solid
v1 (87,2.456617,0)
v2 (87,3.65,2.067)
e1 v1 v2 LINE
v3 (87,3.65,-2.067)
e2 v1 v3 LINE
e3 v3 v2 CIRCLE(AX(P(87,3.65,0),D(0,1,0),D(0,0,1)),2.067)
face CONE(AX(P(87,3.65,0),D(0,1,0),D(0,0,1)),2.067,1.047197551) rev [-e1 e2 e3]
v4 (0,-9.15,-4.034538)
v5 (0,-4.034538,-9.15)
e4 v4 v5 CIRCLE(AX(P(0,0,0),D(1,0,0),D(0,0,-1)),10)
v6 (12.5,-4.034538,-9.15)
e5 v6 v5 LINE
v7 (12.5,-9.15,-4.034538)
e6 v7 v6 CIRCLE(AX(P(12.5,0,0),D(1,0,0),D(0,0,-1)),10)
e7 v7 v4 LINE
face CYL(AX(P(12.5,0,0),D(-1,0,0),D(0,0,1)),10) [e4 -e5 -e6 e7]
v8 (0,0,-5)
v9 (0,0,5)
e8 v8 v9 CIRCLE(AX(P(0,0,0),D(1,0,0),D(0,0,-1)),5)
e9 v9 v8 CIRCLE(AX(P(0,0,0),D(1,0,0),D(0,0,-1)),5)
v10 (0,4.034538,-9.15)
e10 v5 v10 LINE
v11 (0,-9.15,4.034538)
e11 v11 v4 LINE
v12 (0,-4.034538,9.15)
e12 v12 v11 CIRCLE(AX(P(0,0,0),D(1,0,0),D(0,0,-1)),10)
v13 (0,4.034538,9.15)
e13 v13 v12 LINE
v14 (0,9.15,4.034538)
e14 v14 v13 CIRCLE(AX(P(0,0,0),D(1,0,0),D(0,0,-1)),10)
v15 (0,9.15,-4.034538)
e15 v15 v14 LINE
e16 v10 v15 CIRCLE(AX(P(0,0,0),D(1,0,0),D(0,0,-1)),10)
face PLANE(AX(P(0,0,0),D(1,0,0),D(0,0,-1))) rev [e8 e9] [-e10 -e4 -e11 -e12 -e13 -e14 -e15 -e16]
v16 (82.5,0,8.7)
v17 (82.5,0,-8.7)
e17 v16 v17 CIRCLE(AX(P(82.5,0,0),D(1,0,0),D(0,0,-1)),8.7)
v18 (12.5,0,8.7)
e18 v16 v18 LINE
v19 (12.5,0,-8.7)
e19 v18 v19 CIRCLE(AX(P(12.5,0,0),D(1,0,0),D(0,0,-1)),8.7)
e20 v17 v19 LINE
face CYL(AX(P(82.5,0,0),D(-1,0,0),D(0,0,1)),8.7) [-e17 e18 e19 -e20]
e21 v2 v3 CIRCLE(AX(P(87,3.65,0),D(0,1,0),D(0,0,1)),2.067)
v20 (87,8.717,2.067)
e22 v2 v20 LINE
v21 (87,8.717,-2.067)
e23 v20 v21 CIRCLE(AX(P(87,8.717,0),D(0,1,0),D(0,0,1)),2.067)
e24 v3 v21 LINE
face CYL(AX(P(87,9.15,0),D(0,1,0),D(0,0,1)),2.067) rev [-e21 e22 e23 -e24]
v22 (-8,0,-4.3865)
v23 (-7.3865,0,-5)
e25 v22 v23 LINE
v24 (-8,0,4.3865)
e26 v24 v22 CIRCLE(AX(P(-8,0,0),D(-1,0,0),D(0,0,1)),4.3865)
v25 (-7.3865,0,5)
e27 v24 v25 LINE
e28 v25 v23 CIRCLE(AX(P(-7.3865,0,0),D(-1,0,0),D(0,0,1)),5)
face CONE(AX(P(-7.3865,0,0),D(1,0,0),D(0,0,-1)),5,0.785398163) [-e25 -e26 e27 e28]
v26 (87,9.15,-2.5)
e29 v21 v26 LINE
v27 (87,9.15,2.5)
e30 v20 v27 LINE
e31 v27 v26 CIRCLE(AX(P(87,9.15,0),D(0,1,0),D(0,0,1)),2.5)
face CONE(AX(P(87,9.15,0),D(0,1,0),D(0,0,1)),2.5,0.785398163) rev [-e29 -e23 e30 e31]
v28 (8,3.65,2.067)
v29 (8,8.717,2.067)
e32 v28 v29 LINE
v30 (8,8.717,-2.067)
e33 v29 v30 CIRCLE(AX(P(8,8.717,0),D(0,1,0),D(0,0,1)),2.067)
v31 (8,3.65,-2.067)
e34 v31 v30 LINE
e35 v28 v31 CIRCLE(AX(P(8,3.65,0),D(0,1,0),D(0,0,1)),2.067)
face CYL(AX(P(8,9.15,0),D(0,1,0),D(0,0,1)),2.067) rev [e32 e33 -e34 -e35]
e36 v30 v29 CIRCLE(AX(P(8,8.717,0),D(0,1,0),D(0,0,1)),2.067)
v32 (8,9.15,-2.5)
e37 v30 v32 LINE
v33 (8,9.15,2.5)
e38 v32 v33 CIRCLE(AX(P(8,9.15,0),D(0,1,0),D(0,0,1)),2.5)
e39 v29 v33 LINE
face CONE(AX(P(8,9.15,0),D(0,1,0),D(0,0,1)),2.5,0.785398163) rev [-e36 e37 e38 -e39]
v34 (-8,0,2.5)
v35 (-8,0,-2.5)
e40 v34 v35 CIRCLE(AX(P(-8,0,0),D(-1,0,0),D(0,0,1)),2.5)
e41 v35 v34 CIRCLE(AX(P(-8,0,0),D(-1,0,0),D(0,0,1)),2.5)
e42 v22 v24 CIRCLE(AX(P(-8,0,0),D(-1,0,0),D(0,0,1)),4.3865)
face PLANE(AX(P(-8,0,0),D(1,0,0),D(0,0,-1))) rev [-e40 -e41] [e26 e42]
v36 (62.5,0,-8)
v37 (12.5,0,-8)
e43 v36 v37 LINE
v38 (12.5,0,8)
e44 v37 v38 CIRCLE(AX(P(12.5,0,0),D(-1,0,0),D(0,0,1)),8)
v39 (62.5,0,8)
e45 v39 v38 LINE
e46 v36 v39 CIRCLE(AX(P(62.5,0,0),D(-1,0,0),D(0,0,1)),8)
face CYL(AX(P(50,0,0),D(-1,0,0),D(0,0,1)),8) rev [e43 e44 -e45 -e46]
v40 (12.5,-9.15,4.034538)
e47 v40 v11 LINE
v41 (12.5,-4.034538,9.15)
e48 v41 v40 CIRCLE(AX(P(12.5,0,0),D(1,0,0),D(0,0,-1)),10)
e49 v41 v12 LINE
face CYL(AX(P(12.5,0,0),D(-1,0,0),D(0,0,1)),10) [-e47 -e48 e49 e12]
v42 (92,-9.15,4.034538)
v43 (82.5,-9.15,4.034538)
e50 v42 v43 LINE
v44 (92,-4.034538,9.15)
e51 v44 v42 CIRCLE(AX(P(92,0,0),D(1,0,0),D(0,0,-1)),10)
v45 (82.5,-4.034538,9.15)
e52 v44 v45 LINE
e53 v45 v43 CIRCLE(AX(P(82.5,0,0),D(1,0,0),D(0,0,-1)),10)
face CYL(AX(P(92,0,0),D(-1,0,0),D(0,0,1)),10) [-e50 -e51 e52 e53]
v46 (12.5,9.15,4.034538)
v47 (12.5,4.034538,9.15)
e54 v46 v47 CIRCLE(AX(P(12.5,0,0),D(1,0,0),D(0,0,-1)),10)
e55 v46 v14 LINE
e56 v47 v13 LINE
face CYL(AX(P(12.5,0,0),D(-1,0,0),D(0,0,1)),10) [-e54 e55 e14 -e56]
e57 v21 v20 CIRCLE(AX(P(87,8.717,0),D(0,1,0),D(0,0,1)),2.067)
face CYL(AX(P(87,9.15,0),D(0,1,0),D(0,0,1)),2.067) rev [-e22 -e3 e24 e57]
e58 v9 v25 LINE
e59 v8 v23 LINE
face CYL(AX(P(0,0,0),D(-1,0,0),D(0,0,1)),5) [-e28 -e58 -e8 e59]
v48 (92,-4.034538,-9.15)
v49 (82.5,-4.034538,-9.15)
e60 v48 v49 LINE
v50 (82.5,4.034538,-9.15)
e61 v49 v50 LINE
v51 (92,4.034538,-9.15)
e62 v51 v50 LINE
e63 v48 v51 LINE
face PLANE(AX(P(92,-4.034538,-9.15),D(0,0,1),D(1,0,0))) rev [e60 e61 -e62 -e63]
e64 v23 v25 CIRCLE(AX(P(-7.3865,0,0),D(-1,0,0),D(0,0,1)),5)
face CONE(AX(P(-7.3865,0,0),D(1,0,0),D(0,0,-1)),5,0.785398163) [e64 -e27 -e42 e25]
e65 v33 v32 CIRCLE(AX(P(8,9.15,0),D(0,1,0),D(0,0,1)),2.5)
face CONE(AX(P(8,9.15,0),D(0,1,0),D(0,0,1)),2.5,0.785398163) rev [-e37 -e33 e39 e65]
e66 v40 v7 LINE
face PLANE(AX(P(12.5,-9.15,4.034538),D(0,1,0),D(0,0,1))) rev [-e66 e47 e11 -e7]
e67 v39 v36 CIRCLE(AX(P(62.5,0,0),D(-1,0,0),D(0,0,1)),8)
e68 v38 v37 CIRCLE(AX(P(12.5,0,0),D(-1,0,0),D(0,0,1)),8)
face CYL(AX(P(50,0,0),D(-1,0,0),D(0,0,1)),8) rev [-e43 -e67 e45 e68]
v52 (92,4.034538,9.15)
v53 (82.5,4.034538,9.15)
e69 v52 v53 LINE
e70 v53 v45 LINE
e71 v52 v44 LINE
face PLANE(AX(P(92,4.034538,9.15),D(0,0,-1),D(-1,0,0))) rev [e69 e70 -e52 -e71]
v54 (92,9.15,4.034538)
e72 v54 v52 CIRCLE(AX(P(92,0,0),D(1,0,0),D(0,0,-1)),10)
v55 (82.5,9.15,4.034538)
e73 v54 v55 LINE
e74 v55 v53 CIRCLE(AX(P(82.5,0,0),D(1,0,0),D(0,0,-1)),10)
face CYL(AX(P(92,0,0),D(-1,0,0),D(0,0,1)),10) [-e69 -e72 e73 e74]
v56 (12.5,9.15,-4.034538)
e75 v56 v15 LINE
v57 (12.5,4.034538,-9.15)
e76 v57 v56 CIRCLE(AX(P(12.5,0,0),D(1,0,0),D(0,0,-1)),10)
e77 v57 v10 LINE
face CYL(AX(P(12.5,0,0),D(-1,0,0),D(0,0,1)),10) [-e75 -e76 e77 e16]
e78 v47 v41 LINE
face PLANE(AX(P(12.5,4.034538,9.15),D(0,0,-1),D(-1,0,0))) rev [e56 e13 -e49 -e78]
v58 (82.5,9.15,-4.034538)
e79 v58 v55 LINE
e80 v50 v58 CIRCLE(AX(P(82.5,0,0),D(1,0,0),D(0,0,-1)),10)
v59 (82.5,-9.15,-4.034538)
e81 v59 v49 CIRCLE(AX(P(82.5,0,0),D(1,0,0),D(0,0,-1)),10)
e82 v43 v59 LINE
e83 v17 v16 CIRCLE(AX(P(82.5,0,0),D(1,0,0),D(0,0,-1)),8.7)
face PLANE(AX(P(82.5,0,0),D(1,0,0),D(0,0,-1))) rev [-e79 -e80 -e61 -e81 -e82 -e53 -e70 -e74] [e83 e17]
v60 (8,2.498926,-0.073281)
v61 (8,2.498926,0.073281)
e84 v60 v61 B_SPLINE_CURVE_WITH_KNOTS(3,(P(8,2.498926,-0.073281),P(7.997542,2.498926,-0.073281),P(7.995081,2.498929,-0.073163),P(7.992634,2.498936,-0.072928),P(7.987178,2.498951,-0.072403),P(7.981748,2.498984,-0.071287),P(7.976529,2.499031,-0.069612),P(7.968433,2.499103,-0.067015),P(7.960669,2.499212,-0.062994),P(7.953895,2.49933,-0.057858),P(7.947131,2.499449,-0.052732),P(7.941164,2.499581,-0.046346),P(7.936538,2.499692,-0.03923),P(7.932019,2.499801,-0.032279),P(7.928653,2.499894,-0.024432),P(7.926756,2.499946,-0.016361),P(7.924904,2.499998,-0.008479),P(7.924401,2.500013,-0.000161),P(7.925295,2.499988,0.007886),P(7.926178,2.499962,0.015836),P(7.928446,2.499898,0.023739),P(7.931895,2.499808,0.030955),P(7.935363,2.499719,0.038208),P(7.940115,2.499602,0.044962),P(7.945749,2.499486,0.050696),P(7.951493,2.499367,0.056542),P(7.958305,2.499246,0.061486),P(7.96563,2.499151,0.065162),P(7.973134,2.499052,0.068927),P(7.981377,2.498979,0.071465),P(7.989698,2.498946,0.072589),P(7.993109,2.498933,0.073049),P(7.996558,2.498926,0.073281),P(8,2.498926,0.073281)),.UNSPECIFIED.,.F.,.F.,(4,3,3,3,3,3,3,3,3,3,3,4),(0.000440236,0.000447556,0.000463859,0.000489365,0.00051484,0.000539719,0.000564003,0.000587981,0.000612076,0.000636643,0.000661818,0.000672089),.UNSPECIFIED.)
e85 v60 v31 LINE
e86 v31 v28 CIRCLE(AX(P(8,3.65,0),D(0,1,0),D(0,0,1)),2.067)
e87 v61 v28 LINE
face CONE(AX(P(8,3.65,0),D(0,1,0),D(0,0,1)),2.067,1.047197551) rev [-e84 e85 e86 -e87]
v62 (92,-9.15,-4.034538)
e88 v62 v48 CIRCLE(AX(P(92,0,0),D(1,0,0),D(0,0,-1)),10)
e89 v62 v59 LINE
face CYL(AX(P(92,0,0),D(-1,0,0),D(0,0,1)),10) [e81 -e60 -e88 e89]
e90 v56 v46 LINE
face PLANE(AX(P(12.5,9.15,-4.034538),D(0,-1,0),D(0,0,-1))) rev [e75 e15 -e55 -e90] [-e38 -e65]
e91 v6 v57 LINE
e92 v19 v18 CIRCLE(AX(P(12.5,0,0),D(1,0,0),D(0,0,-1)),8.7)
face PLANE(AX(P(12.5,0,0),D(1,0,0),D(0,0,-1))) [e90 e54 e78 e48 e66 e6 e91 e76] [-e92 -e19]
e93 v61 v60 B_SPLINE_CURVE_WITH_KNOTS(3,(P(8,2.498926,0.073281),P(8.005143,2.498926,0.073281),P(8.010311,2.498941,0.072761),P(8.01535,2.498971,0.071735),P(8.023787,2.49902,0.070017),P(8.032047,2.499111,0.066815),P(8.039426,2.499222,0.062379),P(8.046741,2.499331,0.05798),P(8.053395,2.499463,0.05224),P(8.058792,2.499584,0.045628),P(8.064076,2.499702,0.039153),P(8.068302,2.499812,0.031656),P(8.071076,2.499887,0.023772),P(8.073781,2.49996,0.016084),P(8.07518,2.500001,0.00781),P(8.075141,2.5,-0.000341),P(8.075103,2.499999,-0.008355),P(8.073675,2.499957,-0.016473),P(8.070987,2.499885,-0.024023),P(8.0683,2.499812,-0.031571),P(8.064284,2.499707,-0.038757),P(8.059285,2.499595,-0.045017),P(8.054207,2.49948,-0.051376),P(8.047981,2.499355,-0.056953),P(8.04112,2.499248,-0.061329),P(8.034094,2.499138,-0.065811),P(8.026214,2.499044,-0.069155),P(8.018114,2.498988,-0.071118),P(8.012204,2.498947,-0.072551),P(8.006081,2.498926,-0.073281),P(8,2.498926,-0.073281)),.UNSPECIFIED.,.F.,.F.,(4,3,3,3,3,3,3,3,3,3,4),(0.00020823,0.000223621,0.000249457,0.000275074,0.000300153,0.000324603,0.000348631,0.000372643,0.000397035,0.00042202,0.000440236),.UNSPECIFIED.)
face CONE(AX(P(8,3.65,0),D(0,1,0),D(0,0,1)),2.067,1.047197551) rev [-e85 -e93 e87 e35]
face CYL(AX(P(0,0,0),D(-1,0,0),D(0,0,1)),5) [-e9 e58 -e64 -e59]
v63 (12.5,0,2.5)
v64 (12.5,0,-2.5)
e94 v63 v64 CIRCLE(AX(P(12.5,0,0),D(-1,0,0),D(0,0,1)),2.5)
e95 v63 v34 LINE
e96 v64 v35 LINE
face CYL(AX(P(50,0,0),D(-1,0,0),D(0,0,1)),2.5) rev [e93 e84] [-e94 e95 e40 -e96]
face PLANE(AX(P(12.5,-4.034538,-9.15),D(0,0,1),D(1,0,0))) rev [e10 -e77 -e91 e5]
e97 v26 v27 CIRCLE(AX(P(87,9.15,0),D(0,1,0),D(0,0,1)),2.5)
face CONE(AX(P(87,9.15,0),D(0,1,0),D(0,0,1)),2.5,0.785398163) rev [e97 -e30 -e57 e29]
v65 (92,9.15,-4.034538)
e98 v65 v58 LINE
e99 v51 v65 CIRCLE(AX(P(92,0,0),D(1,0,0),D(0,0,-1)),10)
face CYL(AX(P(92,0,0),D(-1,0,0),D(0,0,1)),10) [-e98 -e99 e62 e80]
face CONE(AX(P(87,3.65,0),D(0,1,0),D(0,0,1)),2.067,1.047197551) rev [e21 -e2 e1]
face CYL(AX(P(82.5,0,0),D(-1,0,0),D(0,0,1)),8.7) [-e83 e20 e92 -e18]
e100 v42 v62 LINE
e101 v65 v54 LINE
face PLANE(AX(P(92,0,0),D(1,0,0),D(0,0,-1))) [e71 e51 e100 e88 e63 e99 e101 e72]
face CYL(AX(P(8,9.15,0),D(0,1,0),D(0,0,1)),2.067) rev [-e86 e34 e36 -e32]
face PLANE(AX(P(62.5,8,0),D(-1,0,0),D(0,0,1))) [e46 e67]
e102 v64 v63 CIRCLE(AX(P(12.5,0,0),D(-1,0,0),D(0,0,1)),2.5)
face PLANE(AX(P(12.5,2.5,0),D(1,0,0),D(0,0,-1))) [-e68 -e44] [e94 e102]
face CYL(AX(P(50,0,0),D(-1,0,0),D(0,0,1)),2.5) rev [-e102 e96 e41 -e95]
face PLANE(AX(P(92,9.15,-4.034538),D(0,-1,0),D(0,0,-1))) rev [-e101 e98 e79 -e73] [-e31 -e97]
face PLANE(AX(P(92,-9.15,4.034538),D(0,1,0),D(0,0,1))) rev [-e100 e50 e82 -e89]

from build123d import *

# Parameters (mm, degrees)
BOSS_EXTRUDE1_DEPTH = 12.5
SKETCH3_R           = 8.7
BOSS_EXTRUDE2_DEPTH = 70
BOSS_EXTRUDE3_DEPTH = 9.5
HOLE1_D             = 4.134
HOLE1_DEPTH         = 5.5
HOLE1_CSINK_D       = 5
HOLE1_CSINK_ANGLE   = 90
HOLE1_TIP           = 1.193383006
HOLE2_D             = 4.134
HOLE2_DEPTH         = 5.5
HOLE2_CSINK_D       = 5
HOLE2_CSINK_ANGLE   = 90
HOLE2_TIP           = 1.193383006


with BuildPart() as part:
    # Sketch1 → Revolve1 (revolve)
    with BuildSketch(Plane.XY, mode=Mode.PRIVATE) as revolve1_sk:
        Polygon((-8, 0), (-8, 4.3865), (-7.3865, 5), (0, 5), (0, 0), align=None)
    revolve(revolve1_sk.sketch.rotate(Axis((0, 0, 0), (-1, 0, 0)), 270), axis=Axis((0, 0, 0), (-1, 0, 0)))

    # Sketch2 → Boss-Extrude1 (add)
    with BuildSketch(Plane(origin=(0, 0, 0), x_dir=(0, 0, -1), z_dir=(1, 0, 0))):
        with BuildLine():
            Line((-4.034538387, -9.15), (4.034538387, -9.15))
            ThreePointArc((4.034538387, -9.15), (7.071067812, -7.071067812), (9.15, -4.034538387))
            Line((9.15, -4.034538387), (9.15, 4.034538387))
            ThreePointArc((9.15, 4.034538387), (7.071067812, 7.071067812), (4.034538387, 9.15))
            Line((4.034538387, 9.15), (-4.034538387, 9.15))
            ThreePointArc((-4.034538387, 9.15), (-7.071067812, 7.071067812), (-9.15, 4.034538387))
            Line((-9.15, 4.034538387), (-9.15, -4.034538387))
            ThreePointArc((-9.15, -4.034538387), (-7.071067812, -7.071067812), (-4.034538387, -9.15))
        make_face()
    extrude(amount=BOSS_EXTRUDE1_DEPTH)

    # Sketch3 → Boss-Extrude2 (add)
    with BuildSketch(Plane(origin=(12.5, 0, 0), x_dir=(0, 0, -1), z_dir=(1, 0, 0))):
        Circle(SKETCH3_R)
    extrude(amount=BOSS_EXTRUDE2_DEPTH)

    # Sketch4 → Boss-Extrude3 (add)
    with BuildSketch(Plane(origin=(82.5, 0, 0), x_dir=(0, 0, -1), z_dir=(1, 0, 0))):
        with BuildLine():
            Line((-4.034538387, -9.15), (4.034538387, -9.15))
            ThreePointArc((4.034538387, -9.15), (7.071067812, -7.071067812), (9.15, -4.034538387))
            Line((9.15, -4.034538387), (9.15, 4.034538387))
            ThreePointArc((9.15, 4.034538387), (7.071067812, 7.071067812), (4.034538387, 9.15))
            Line((4.034538387, 9.15), (-4.034538387, 9.15))
            ThreePointArc((-4.034538387, 9.15), (-7.071067812, 7.071067812), (-9.15, 4.034538387))
            Line((-9.15, 4.034538387), (-9.15, -4.034538387))
            ThreePointArc((-9.15, -4.034538387), (-7.071067812, -7.071067812), (-4.034538387, -9.15))
        make_face()
    extrude(amount=BOSS_EXTRUDE3_DEPTH)

    # Hole1
    with Locations(Plane(origin=(0, 9.15, 0), x_dir=(1, 0, 0), z_dir=(0, 1, 0))):
        with Locations((8, 0)):
            CounterSinkHole(HOLE1_D / 2, HOLE1_CSINK_D / 2, depth=HOLE1_DEPTH, counter_sink_angle=HOLE1_CSINK_ANGLE)
            with Locations((0, 0, -(HOLE1_DEPTH + HOLE1_TIP / 2))):  # 120° drill point
                Cone(0, HOLE1_D / 2, HOLE1_TIP, mode=Mode.SUBTRACT)

    # Hole2
    with Locations(Plane(origin=(0, 9.15, 0), x_dir=(1, 0, 0), z_dir=(0, 1, 0))):
        with Locations((87, 0)):
            CounterSinkHole(HOLE2_D / 2, HOLE2_CSINK_D / 2, depth=HOLE2_DEPTH, counter_sink_angle=HOLE2_CSINK_ANGLE)
            with Locations((0, 0, -(HOLE2_DEPTH + HOLE2_TIP / 2))):  # 120° drill point
                Cone(0, HOLE2_D / 2, HOLE2_TIP, mode=Mode.SUBTRACT)

    # Sketch9 → Cut-Revolve1 (revolve, cut)
    with BuildSketch(Plane.XY, mode=Mode.PRIVATE) as cut_revolve1_sk:
        Polygon((-8, 0), (-8, 2.5), (12.5, 2.5), (12.5, 8), (62.5, 8), (62.5, 0), align=None)
    revolve(cut_revolve1_sk.sketch.rotate(Axis((50, 0, 0), (-1, 0, 0)), 270), axis=Axis((50, 0, 0), (-1, 0, 0)), mode=Mode.SUBTRACT)


solid = part.part
